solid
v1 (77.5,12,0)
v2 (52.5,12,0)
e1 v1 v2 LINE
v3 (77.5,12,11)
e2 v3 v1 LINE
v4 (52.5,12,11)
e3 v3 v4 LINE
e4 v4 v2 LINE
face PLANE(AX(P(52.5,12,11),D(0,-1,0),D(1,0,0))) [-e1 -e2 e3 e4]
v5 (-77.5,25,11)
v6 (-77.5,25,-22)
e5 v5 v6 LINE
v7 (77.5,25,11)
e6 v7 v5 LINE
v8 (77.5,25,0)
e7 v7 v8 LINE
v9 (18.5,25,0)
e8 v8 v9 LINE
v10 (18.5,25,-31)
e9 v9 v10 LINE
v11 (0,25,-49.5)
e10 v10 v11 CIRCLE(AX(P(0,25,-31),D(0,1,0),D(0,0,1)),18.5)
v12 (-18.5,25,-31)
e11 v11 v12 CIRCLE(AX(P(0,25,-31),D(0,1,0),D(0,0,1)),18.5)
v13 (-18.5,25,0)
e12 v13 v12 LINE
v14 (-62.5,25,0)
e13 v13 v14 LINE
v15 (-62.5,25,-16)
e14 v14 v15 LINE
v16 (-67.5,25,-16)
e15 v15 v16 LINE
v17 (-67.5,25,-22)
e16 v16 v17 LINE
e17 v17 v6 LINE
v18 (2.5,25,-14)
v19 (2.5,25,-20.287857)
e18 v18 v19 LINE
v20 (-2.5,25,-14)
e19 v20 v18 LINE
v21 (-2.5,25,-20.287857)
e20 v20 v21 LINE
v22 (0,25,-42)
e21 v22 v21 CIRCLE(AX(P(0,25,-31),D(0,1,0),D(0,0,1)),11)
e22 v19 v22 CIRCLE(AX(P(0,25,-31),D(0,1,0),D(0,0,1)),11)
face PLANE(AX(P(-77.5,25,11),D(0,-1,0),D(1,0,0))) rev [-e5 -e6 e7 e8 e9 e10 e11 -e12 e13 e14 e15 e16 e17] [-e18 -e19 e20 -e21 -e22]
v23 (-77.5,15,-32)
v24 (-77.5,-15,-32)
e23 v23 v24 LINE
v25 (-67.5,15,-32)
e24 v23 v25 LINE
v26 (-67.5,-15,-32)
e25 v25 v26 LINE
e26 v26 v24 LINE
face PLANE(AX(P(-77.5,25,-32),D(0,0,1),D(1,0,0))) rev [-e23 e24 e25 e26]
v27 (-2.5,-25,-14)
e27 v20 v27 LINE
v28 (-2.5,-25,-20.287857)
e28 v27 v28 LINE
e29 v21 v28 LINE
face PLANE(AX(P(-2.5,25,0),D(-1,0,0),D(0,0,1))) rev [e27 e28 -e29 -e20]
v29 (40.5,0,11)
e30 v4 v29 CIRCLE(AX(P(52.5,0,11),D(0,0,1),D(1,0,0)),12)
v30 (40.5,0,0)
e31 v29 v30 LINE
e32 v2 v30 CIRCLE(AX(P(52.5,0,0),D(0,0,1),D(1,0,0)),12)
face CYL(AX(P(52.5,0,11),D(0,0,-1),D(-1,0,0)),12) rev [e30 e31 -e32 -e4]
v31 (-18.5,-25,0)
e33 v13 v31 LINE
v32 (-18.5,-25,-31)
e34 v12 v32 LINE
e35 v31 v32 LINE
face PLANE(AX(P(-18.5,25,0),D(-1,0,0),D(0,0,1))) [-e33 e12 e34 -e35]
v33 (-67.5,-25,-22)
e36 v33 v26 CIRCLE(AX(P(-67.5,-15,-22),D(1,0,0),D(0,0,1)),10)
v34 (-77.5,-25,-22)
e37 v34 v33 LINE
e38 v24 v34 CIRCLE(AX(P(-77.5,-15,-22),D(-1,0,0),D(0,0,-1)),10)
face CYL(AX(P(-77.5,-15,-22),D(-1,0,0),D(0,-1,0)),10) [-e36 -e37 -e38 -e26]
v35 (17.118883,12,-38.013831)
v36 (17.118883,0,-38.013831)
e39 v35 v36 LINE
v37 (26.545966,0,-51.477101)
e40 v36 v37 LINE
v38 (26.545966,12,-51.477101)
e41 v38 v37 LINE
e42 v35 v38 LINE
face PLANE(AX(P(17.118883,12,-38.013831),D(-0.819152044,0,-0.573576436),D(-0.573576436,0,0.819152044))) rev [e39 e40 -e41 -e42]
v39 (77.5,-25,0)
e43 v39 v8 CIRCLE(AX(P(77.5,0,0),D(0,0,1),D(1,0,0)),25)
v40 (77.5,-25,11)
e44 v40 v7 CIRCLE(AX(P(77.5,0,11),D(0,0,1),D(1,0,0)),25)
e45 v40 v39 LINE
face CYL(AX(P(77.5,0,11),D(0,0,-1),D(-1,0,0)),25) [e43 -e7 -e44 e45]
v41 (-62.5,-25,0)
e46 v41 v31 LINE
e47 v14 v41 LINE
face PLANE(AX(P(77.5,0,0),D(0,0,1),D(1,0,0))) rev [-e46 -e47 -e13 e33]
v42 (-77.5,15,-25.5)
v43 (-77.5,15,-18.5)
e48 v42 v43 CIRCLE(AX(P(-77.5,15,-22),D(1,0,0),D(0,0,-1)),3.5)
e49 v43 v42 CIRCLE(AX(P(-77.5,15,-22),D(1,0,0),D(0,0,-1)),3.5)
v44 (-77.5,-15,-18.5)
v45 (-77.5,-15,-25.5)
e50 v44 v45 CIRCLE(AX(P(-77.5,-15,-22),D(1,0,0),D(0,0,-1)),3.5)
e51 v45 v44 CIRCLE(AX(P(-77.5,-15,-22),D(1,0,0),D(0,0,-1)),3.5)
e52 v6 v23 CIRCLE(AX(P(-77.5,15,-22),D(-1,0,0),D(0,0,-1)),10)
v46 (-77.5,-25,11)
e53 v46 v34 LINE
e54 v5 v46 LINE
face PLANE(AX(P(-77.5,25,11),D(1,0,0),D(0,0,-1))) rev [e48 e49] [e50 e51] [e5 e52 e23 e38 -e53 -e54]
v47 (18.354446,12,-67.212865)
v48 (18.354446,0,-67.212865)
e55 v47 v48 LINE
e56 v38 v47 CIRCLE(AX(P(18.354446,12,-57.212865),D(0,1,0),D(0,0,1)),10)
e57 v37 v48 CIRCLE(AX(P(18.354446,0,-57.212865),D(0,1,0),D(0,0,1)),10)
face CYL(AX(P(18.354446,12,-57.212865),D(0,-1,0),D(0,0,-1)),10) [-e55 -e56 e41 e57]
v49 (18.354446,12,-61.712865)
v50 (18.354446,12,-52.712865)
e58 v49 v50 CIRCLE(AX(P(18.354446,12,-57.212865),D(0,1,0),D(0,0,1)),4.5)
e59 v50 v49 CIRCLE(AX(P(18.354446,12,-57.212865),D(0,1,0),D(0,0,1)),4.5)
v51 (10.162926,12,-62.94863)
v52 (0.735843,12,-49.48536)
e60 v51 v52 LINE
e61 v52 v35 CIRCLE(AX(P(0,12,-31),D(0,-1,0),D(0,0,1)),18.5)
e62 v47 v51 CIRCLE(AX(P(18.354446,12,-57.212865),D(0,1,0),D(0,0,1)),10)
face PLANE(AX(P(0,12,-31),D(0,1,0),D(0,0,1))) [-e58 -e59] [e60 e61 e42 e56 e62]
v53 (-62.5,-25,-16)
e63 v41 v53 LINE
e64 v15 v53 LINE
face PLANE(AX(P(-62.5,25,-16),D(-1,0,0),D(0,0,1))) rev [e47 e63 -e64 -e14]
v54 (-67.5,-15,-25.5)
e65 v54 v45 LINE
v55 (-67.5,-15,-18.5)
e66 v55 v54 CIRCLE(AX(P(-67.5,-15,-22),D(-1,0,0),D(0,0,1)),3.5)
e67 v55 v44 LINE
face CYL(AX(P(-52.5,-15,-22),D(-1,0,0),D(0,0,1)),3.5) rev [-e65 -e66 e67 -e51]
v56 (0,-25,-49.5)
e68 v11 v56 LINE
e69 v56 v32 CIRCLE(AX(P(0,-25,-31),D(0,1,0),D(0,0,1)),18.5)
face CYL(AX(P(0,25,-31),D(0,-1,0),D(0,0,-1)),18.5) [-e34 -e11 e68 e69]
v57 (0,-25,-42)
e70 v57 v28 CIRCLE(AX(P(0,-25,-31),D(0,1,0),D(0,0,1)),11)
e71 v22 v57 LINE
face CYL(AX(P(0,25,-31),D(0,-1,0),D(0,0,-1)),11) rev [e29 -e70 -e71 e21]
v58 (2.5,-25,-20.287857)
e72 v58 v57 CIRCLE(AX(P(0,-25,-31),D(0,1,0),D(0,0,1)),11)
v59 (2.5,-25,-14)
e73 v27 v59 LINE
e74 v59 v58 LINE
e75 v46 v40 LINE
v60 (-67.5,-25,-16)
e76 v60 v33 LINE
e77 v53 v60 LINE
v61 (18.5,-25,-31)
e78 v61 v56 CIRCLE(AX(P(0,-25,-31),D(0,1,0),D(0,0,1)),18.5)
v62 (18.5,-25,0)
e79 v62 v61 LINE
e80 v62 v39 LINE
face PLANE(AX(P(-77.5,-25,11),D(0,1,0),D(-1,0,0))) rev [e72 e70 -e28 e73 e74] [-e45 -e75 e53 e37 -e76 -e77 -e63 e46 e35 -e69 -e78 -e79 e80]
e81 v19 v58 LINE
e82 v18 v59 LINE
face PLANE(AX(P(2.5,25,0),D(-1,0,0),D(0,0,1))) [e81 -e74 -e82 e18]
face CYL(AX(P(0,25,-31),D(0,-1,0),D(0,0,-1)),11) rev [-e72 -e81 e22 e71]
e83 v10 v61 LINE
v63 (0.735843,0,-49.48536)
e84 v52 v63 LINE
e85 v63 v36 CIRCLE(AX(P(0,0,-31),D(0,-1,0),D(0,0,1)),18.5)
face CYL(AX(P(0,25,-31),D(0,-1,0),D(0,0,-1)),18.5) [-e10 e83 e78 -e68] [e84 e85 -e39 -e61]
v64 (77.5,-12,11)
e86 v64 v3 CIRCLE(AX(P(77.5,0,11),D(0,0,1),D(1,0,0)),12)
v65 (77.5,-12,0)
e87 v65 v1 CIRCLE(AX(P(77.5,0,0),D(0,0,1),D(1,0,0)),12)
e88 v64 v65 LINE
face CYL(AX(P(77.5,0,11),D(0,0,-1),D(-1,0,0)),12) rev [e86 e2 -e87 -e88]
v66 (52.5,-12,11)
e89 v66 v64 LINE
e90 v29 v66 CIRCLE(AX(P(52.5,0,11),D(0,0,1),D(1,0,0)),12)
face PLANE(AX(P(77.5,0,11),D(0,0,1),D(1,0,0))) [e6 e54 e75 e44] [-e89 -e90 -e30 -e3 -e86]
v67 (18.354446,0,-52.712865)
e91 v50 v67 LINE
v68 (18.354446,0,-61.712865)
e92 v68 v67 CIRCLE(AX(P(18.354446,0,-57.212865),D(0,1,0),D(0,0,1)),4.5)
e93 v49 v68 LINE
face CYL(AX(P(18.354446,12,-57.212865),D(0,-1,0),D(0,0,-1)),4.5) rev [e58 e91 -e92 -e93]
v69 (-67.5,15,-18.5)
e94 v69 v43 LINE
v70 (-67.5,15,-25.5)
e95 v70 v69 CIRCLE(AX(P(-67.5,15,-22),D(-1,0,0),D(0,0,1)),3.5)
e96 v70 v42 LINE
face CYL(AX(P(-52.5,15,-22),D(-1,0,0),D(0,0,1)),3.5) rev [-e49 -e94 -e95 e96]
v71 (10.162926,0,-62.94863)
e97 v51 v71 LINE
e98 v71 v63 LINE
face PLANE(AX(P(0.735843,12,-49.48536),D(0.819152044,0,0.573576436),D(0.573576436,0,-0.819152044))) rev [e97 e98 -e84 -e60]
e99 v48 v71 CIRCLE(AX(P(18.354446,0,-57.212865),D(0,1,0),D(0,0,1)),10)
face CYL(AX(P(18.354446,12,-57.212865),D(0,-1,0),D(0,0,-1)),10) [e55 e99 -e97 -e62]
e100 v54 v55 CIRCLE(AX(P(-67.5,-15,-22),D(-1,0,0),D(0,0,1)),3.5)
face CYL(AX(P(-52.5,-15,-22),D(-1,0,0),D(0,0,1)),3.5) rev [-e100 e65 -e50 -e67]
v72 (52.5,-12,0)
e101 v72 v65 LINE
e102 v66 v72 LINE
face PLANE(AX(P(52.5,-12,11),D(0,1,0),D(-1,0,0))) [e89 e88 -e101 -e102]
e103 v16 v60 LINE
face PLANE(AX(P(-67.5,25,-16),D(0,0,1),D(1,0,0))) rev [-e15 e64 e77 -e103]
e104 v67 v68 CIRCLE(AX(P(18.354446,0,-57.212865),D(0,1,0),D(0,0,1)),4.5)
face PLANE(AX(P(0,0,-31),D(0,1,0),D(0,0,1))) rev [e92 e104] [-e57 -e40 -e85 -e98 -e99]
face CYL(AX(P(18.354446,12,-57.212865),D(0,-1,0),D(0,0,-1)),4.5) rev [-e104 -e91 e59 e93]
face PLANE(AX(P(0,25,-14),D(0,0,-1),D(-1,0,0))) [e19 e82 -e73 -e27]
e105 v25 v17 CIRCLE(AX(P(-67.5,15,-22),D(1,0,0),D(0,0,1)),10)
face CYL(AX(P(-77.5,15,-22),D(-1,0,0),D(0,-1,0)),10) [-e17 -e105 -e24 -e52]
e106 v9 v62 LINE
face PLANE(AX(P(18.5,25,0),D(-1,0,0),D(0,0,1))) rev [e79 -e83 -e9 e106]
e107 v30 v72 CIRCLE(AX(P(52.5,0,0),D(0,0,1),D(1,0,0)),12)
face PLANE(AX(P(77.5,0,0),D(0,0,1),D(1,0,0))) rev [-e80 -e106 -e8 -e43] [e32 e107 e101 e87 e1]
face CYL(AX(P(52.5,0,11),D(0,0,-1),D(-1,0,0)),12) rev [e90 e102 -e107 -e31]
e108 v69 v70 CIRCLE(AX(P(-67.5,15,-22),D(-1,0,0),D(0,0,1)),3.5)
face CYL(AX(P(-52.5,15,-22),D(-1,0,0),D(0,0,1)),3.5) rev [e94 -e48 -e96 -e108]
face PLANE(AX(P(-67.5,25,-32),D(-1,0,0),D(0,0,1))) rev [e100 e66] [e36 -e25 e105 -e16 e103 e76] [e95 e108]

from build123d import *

# Parameters (mm, degrees)
SLOTTED_ARM_PLATE_DEPTH   = 11
END_WALL_DEPTH            = 25
END_WALL_FILLET_R10_R     = 10
WALL_NOTCH_SKETCH_R       = 3.5
WALL_NOTCH_CUT_DEPTH      = 25
HUB_WITH_KEYED_BORE_DEPTH = 25
EYE_START                 = 12
EYE_LUG_SKETCH_R          = 4.5
EYE_LUG_DEPTH             = 12


with BuildPart() as part:
    # Slotted Arm Sketch → Slotted Arm Plate (new body)
    with BuildSketch(Plane.XY):
        with BuildLine():
            Line((-77.5, 25), (77.5, 25))
            ThreePointArc((77.5, 25), (102.5, 0), (77.5, -25))
            Line((77.5, -25), (-77.5, -25))
            Line((-77.5, -25), (-77.5, 25))
        make_face()
        with BuildLine():
            Line((52.5, 12), (77.5, 12))
            ThreePointArc((77.5, 12), (89.5, 0), (77.5, -12))
            Line((77.5, -12), (52.5, -12))
            ThreePointArc((52.5, -12), (40.5, 0), (52.5, 12))
        make_face(mode=Mode.SUBTRACT)
    extrude(amount=SLOTTED_ARM_PLATE_DEPTH)

    # End Wall Sketch → End Wall (add, symmetric)
    with BuildSketch(Plane(origin=(0, 0, 0), x_dir=(1, 0, 0), z_dir=(0, 1, 0))):
        Polygon((-77.5, 0), (-77.5, 32), (-67.5, 32), (-67.5, 16), (-62.5, 16), (-62.5, 0), align=None)
    extrude(amount=END_WALL_DEPTH, both=True)

    # End Wall Fillet R10
    end_wall_fillet_r10_edges = [part.edges().sort_by_distance(p)[0] for p in [
        (-72.5, -25, -32),
        (-72.5, 25, -32),
    ]]
    fillet(end_wall_fillet_r10_edges, radius=END_WALL_FILLET_R10_R)

    # Wall Notch Sketch → Wall Notch Cut (cut, symmetric)
    with BuildSketch(Plane.ZY.offset(77.5)):
        with Locations((-22, 15)):
            Circle(WALL_NOTCH_SKETCH_R)
        with Locations((-22, -15)):
            Circle(WALL_NOTCH_SKETCH_R)
    extrude(amount=WALL_NOTCH_CUT_DEPTH, both=True, mode=Mode.SUBTRACT)

    # Hub Sketch → Hub With Keyed Bore (add, symmetric)
    with BuildSketch(Plane(origin=(0, 0, 0), x_dir=(1, 0, 0), z_dir=(0, 1, 0))):
        with BuildLine():
            Line((18.5, 0), (18.5, 31))
            ThreePointArc((18.5, 31), (0, 49.5), (-18.5, 31))
            Line((-18.5, 31), (-18.5, 0))
            Line((-18.5, 0), (18.5, 0))
        make_face()
        with BuildLine():
            ThreePointArc((2.5, 20.287857357), (0, 42), (-2.5, 20.287857357))
            Line((-2.5, 20.287857357), (-2.5, 14))
            Line((-2.5, 14), (2.5, 14))
            Line((2.5, 14), (2.5, 20.287857357))
        make_face(mode=Mode.SUBTRACT)
    extrude(amount=HUB_WITH_KEYED_BORE_DEPTH, both=True)

    # Eye Lug Sketch → Eye Lug (add)
    with BuildSketch(Plane(origin=(0, 0, 0), x_dir=(1, 0, 0), z_dir=(0, 1, 0)).offset(EYE_START)):
        with BuildLine():
            Line((17.118883443, 38.013831311), (26.545966406, 51.477101054))
            ThreePointArc((26.545966406, 51.477101054), (24.090210327, 65.40438586), (10.16292552, 62.948629781))
            Line((10.16292552, 62.948629781), (0.735842557, 49.485360038))
            ThreePointArc((0.735842557, 49.485360038), (10.611164072, 46.154312819), (17.118883443, 38.013831311))
        make_face()
        with Locations(Location((18.354445963, 57.212865417, 0), (0, 0, 270))):
            Circle(EYE_LUG_SKETCH_R, mode=Mode.SUBTRACT)
    extrude(amount=-EYE_LUG_DEPTH)


solid = part.part
